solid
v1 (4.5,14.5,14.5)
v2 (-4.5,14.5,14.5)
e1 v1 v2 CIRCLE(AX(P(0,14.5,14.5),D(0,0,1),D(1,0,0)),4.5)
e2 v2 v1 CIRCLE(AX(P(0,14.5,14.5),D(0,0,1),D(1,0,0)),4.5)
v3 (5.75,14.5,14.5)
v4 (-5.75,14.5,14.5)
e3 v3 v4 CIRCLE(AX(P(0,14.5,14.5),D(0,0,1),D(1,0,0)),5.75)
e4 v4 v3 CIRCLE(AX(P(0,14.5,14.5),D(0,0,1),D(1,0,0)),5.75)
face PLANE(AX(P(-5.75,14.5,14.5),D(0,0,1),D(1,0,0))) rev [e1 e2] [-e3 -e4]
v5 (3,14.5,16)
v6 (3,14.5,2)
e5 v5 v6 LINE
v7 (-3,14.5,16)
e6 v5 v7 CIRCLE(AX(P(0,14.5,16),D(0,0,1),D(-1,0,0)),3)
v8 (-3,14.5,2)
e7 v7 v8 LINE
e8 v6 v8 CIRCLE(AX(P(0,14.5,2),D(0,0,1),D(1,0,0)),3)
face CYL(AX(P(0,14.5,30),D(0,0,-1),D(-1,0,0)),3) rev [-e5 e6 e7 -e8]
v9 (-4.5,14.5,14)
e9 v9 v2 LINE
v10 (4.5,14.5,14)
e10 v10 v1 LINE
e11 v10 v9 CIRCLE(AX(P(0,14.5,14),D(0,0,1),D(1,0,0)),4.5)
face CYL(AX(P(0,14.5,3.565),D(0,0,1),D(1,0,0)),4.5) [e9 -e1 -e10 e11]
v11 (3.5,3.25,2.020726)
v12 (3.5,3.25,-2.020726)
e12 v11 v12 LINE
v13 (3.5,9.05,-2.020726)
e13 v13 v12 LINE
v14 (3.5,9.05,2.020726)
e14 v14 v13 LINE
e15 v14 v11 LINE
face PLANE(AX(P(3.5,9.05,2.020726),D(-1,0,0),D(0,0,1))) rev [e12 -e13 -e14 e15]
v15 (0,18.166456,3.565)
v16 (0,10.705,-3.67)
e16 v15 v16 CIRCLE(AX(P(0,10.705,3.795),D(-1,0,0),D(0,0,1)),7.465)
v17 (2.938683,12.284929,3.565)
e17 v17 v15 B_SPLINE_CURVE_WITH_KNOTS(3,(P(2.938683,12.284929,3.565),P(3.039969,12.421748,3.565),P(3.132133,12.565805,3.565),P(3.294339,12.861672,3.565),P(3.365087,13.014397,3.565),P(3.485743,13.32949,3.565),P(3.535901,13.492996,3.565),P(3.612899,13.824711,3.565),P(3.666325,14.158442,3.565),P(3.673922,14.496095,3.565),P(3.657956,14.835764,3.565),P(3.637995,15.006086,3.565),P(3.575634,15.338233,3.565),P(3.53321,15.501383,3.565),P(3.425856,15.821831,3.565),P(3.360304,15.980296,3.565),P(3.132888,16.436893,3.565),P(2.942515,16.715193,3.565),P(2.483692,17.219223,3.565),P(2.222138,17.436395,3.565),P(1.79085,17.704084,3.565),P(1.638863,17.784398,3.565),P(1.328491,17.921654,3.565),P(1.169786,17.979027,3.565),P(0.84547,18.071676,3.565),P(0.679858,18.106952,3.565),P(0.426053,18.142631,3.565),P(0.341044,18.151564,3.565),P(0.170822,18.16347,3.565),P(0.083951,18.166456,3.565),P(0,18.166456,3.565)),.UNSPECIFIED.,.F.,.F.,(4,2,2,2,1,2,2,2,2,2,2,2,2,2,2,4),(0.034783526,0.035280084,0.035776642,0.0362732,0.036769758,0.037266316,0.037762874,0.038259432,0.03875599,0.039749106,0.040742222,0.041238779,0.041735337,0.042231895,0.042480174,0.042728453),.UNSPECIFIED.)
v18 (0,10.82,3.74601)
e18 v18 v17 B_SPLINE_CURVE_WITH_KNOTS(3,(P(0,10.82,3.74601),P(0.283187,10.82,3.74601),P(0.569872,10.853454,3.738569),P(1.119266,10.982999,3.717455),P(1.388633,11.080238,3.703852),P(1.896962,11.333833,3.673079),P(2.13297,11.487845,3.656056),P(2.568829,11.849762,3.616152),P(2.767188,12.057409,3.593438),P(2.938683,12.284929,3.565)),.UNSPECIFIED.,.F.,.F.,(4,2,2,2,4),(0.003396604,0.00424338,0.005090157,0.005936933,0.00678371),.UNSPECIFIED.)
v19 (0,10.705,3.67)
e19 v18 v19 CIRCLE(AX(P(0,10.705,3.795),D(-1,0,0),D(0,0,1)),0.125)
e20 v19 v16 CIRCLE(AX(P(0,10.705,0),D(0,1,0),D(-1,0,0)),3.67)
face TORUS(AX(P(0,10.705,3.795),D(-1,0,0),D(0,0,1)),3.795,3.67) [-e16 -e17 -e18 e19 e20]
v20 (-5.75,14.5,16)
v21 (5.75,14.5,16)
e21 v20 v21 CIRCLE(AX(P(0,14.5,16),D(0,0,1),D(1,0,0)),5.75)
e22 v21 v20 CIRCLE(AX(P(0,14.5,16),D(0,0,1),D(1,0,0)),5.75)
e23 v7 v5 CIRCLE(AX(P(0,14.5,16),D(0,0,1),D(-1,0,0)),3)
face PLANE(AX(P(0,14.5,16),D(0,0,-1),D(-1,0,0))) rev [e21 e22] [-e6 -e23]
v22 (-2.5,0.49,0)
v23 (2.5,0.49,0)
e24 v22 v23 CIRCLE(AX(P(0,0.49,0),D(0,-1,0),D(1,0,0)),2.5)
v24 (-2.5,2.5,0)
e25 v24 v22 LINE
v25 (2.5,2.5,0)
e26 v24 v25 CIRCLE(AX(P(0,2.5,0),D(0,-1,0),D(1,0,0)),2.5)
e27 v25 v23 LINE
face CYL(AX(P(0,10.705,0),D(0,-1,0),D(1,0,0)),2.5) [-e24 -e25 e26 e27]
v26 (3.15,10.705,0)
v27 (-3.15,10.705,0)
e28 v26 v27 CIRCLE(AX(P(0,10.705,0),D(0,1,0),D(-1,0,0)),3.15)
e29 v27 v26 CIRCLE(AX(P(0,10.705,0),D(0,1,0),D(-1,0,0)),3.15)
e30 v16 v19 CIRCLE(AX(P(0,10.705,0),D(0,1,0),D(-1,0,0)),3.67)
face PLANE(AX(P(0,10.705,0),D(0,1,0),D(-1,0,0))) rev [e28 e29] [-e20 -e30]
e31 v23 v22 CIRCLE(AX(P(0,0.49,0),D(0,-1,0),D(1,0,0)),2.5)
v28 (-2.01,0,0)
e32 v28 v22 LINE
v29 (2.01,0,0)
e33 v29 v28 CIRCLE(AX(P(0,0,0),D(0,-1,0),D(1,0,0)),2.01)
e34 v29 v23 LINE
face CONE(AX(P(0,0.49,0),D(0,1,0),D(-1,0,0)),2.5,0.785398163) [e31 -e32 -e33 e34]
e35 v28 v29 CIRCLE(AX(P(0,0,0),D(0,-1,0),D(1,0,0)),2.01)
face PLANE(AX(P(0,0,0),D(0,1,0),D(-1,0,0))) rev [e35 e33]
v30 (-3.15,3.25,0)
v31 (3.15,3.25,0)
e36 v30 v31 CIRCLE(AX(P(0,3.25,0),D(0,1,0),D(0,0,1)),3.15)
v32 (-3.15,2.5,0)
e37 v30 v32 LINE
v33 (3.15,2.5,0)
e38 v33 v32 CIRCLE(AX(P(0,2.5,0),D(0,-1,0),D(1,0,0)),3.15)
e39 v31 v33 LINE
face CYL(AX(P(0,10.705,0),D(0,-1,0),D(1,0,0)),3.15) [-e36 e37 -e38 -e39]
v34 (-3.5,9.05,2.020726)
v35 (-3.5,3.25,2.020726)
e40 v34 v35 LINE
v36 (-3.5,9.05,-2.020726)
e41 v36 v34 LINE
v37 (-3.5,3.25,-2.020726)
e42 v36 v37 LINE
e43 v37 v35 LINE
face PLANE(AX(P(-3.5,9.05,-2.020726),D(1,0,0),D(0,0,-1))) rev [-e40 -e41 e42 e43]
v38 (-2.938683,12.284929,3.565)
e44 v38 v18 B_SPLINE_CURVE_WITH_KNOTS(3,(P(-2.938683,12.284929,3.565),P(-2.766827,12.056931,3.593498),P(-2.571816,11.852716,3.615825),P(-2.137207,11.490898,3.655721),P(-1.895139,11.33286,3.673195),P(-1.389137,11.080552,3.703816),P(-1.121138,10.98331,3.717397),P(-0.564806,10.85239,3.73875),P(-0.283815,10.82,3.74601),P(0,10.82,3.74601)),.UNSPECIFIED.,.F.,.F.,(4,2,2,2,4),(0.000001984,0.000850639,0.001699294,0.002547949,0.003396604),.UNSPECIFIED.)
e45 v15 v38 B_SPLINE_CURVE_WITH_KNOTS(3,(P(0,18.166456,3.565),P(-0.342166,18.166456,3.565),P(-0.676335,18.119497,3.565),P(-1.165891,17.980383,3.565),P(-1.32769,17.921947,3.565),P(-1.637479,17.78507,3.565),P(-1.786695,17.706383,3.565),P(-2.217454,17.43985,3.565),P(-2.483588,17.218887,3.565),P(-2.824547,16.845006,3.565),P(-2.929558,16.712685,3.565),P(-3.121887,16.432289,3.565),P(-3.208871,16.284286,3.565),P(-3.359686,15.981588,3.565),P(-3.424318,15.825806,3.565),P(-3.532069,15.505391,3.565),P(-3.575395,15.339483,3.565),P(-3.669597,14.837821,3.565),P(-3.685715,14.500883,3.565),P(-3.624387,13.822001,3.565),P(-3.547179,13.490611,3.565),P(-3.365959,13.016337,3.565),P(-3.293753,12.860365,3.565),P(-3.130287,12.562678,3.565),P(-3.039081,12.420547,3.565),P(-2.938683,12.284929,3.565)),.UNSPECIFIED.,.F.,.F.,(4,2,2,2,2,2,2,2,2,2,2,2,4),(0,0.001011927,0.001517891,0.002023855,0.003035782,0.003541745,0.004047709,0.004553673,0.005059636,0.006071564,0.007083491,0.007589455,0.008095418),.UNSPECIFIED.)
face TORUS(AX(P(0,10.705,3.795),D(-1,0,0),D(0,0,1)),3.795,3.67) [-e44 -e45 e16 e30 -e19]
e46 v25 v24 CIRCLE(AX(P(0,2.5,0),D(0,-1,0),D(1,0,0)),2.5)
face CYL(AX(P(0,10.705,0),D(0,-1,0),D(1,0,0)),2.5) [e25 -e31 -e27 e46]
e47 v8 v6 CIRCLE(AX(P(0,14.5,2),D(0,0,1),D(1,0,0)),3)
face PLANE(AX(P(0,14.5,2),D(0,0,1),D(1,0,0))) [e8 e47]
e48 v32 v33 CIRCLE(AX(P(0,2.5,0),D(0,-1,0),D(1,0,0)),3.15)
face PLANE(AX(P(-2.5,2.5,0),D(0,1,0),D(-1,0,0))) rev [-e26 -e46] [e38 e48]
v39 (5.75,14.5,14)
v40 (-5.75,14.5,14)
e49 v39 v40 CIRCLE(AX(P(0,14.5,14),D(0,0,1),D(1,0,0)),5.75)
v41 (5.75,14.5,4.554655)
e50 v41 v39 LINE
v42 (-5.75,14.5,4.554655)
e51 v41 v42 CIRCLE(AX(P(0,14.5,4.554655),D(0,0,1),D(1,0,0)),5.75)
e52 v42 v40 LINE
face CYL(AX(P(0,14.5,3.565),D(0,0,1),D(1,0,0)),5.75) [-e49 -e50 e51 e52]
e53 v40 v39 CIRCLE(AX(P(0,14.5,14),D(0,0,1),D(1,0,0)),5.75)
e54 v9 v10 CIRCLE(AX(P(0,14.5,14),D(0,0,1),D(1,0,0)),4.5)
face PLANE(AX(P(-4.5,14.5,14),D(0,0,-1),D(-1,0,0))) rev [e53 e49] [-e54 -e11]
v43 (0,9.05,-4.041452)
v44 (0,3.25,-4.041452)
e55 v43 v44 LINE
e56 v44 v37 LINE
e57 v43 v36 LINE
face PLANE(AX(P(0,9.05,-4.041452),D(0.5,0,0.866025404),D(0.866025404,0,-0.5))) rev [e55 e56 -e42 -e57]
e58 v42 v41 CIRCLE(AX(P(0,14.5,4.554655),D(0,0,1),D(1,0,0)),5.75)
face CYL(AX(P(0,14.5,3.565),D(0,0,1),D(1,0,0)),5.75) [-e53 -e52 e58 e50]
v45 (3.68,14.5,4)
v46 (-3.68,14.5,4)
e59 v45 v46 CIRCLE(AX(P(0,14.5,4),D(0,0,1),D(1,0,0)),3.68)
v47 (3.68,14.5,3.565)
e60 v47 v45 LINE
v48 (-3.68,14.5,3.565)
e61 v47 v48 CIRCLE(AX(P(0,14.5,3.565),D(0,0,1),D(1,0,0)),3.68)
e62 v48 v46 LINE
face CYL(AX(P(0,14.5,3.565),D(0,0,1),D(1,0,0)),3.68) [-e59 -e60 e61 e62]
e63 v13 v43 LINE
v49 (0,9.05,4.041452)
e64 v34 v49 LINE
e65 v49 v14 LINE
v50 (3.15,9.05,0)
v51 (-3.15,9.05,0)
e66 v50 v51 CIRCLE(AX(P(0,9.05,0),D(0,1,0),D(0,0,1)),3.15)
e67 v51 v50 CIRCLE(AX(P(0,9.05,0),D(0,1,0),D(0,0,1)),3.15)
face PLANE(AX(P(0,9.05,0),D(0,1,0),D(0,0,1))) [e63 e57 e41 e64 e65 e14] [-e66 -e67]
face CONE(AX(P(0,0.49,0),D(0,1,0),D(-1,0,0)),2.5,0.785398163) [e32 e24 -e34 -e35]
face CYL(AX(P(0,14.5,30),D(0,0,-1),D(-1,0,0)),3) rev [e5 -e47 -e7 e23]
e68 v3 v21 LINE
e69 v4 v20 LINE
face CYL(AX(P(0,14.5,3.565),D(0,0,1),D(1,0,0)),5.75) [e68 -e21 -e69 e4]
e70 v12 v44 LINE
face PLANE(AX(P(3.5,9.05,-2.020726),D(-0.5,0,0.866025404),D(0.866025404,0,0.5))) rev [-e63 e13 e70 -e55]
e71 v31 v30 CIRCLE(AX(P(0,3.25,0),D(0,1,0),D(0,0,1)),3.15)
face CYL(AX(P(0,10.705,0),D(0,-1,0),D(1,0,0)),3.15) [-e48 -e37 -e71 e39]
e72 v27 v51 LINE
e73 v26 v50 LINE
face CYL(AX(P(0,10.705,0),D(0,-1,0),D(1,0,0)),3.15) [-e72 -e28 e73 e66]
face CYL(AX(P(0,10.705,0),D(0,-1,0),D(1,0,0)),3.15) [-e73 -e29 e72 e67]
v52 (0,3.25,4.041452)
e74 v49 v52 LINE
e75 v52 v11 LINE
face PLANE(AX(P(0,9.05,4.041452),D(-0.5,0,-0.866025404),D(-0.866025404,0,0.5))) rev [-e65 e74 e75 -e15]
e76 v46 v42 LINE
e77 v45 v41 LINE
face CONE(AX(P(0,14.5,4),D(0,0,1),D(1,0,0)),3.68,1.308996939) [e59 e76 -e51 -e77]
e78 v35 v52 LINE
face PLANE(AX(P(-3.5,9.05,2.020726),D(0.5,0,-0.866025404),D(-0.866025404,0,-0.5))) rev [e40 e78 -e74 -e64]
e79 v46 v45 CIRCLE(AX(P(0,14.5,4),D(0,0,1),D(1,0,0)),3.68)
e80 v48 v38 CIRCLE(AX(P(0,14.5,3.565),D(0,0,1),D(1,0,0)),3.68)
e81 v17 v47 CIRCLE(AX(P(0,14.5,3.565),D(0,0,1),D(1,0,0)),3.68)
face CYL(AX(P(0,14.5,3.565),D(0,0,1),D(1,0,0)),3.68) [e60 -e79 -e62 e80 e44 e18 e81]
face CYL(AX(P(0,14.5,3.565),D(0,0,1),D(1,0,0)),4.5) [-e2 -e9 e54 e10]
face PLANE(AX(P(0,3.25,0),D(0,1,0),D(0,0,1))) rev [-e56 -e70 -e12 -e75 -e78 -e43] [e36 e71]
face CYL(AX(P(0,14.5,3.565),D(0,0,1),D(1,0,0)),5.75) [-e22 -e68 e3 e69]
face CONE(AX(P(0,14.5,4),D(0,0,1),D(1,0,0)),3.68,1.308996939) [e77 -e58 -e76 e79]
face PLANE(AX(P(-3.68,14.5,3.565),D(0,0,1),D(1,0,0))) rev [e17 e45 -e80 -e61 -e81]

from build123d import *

# Parameters (mm, degrees)
SKETCH_3_R               = 3.67
REVOLVE_2_ANGLE          = 90
EXTRUDE_1_DEPTH          = 5.8
CUT_EXTRUDE_1_DEPTH      = 14
CUT_EXTRUDE_1_DEPTH_BACK = 14
SKETCH_5_R               = 3


with BuildPart() as part:
    # 草图1 → 旋转1 (revolve)
    with BuildSketch(Plane.XY, mode=Mode.PRIVATE) as revolve_1_sk:
        Polygon((0, 0), (-2.01, 0), (-2.5, 0.49), (-2.5, 2.5), (-3.15, 2.5), (-3.15, 10.705), (0, 10.705), align=None)
    revolve(revolve_1_sk.sketch.rotate(Axis((0, 10.705, 0), (0, -1, 0)), 180), axis=Axis((0, 10.705, 0), (0, -1, 0)))

    # 草图3 → 旋转2 (revolve)
    with BuildSketch(Plane(origin=(0, 10.705, 0), x_dir=(1, 0, 0), z_dir=(0, 1, 0))):
        Circle(SKETCH_3_R)
    revolve(axis=Axis((3.68, 10.705, 3.795), (1, 0, 0)), revolution_arc=REVOLVE_2_ANGLE)

    # 草图4 → 凸台-拉伸1 (add)
    with BuildSketch(Plane(origin=(0, 3.25, 0), x_dir=(1, 0, 0), z_dir=(0, 1, 0))):
        Polygon((-3.5, 2.020725942), (-3.5, -2.020725942), (0, -4.041451884), (3.5, -2.020725942), (3.5, 2.020725942), (0, 4.041451884), align=None)
    extrude(amount=EXTRUDE_1_DEPTH)

    # 草图2 → 旋转3 (revolve)
    with BuildSketch(Plane(origin=(0, 14.5, 0), x_dir=(1, 0, 0), z_dir=(0, 1, 0)), mode=Mode.PRIVATE) as revolve_3_sk:
        Polygon((0, -16), (-5.75, -16), (-5.75, -14.5), (-4.5, -14.5), (-4.5, -14), (-5.75, -14), (-5.75, -4.554654828), (-3.68, -4), (-3.68, -3.565), (0, -3.565), align=None)
    revolve(revolve_3_sk.sketch.rotate(Axis((0, 14.5, 3.565), (0, 0, 1)), 180), axis=Axis((0, 14.5, 3.565), (0, 0, 1)))

    # 草图5 → 切除-拉伸1 (cut, two sides: drawn at the far end of the back side and taken through both)
    with BuildSketch(Plane.XY.offset(16).offset(-CUT_EXTRUDE_1_DEPTH_BACK)):
        with Locations(Location((0, 14.5, 0), (0, 0, 180))):
            Circle(SKETCH_5_R)
    extrude(amount=CUT_EXTRUDE_1_DEPTH + CUT_EXTRUDE_1_DEPTH_BACK, mode=Mode.SUBTRACT)


solid = part.part
